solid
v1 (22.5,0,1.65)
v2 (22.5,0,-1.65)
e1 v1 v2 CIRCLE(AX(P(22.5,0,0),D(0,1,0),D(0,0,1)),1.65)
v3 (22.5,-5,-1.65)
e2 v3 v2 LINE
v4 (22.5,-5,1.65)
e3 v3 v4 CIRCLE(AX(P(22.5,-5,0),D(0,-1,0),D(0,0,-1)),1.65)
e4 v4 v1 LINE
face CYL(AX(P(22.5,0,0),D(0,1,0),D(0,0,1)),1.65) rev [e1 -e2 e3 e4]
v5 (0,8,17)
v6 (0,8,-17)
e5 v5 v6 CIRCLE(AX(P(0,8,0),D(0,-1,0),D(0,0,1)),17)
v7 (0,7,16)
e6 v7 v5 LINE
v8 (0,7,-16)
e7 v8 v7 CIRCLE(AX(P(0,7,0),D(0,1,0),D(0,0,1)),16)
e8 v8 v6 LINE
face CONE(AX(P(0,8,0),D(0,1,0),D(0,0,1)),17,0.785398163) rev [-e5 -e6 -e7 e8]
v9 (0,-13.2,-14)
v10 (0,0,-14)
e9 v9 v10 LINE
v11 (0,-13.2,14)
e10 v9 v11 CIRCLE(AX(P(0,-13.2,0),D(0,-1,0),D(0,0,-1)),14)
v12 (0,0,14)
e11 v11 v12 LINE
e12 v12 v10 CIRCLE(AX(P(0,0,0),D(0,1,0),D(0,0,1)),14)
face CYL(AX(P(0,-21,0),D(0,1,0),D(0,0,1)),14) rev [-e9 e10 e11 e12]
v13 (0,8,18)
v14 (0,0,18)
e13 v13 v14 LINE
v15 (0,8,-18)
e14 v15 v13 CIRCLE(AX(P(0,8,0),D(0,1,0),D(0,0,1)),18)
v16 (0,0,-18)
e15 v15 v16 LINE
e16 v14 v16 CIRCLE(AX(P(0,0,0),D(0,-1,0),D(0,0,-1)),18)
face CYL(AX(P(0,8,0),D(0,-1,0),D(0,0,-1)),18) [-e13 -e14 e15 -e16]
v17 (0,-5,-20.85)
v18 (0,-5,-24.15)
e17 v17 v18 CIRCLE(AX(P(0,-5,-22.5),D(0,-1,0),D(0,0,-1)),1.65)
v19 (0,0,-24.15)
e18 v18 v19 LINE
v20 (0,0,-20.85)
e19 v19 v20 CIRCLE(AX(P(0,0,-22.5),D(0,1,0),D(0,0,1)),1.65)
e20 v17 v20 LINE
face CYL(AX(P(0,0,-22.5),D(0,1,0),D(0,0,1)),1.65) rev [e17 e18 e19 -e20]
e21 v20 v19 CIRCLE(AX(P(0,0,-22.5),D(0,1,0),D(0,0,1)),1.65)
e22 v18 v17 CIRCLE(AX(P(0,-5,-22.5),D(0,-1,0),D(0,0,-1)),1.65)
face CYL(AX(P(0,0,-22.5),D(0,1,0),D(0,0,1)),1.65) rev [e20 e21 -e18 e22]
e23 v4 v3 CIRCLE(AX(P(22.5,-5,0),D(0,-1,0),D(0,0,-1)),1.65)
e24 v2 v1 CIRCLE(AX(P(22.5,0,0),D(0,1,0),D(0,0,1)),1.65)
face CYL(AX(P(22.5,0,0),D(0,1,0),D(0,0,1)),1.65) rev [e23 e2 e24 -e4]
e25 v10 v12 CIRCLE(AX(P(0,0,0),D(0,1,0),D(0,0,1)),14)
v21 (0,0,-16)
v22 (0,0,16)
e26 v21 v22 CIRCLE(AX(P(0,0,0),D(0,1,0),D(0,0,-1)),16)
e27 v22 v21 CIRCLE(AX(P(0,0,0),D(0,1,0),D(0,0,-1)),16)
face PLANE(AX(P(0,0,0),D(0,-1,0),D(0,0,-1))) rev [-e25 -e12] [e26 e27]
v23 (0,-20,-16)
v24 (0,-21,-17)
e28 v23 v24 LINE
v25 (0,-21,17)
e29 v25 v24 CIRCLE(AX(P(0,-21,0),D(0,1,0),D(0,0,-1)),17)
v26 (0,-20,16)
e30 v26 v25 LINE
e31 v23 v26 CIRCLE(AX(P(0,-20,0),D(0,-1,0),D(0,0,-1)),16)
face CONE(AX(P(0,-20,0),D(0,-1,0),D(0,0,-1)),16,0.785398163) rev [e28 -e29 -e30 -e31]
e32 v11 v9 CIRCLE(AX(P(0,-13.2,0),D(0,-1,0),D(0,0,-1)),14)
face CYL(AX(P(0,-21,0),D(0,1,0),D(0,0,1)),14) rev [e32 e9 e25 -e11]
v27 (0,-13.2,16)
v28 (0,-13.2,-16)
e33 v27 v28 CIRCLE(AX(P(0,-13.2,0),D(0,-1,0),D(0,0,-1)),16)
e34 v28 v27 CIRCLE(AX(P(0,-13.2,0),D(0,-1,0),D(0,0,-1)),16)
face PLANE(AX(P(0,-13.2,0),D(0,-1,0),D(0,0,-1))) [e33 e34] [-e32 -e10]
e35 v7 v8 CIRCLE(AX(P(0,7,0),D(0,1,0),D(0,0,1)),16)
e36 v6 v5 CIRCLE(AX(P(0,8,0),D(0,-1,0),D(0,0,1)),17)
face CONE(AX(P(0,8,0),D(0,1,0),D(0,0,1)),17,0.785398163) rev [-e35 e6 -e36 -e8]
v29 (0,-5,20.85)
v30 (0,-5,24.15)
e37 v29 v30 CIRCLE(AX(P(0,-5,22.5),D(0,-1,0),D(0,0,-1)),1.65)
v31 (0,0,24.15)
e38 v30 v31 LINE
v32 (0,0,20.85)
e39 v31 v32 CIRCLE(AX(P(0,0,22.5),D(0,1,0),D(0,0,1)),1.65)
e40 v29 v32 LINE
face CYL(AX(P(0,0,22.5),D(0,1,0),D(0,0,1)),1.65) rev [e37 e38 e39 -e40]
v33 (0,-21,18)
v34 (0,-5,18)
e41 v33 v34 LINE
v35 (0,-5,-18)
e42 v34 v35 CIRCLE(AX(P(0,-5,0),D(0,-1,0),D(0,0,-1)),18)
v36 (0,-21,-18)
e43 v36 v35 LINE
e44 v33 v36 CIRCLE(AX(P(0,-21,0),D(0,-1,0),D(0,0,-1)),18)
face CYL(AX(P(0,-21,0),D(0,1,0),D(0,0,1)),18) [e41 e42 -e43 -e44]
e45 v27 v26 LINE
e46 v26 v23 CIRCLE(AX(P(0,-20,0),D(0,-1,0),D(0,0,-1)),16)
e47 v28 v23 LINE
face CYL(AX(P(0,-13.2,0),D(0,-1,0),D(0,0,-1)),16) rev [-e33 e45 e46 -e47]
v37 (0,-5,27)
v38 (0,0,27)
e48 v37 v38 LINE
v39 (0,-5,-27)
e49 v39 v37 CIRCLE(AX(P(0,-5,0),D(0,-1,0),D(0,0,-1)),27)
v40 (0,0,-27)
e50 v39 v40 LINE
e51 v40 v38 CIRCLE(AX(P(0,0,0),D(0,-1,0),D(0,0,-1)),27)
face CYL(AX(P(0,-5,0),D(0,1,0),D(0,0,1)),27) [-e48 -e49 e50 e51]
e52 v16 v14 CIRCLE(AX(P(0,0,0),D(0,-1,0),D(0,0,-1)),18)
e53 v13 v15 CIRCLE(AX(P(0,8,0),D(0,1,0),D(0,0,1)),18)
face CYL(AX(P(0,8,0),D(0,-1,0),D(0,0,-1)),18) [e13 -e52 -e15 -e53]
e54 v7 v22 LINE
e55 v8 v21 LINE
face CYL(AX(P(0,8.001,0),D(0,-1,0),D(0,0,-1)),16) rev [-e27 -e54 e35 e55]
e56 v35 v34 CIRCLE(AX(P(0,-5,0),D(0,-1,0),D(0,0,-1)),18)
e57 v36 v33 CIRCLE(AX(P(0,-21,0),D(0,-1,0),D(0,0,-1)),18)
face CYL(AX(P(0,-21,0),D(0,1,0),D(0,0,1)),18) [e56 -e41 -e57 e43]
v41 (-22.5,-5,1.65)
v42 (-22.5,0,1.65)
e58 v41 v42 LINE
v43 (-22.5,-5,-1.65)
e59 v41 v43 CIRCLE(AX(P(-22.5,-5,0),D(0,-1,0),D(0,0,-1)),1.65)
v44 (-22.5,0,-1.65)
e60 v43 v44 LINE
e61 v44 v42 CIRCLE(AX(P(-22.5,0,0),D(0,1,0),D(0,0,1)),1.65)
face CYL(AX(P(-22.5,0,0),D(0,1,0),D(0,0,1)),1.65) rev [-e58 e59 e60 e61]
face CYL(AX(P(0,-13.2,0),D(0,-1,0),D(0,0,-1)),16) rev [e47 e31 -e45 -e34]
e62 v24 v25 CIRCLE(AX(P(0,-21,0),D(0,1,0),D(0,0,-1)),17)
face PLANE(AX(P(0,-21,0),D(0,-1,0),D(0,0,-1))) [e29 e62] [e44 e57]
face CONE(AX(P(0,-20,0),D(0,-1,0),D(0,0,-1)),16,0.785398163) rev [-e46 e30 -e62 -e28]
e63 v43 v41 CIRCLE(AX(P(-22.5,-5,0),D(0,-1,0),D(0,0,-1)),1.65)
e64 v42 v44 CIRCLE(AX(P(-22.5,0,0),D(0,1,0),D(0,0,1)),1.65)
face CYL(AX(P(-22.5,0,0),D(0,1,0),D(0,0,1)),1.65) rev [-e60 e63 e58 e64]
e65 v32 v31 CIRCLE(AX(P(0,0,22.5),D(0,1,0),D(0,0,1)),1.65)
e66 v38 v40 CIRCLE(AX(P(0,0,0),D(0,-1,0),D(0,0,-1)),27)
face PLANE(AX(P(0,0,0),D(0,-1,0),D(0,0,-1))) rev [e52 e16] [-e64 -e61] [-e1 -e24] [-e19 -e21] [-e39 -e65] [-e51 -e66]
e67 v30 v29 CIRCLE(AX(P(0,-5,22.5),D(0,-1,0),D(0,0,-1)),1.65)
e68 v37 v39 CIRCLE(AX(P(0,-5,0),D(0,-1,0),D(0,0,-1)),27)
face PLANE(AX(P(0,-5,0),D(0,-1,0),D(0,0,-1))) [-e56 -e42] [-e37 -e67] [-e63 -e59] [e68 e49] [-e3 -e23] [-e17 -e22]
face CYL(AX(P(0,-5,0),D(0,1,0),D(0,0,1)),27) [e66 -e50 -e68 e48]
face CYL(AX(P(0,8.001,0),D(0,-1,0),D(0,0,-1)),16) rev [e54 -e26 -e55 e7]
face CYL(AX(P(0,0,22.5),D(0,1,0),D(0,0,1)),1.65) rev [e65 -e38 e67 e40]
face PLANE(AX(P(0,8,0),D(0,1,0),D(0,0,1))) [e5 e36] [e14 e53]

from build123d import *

# Parameters (mm, degrees)
SKETCH1_R             = 18
BOSS_EXTRUDE1_DEPTH   = 8
CUT_EXTRUDE1_REACH    = 28.683
SKETCH2_R             = 16
SKETCH3_R             = 27
BOSS_EXTRUDE2_DEPTH   = 5
BOSS_EXTRUDE3_START   = 16
SKETCH4_R             = 18
BOSS_EXTRUDE3_DEPTH   = 16
SKETCH5_R             = 16
CUT_EXTRUDE2_DEPTH    = 7.8
SKETCH6_R             = 14
CUT_EXTRUDE3_DEPTH    = 44.577517139
M4_TAPPED_HOLE1_D     = 3.3
M4_TAPPED_HOLE1_DEPTH = 11.5
M4_TAPPED_HOLE1_TIP   = 0.991420021
CHAMFER1_SIZE         = 1


with BuildPart() as part:
    # Sketch1 → Boss-Extrude1 (new body)
    with BuildSketch(Plane(origin=(0, 0, 0), x_dir=(1, 0, 0), z_dir=(0, 1, 0))):
        with Locations(Location((0, 0, 0), (0, 0, 270))):
            Circle(SKETCH1_R)
    extrude(amount=BOSS_EXTRUDE1_DEPTH)

    # Sketch2 → Cut-Extrude1 (cut, up to next)
    with BuildSketch(Plane.XZ, mode=Mode.PRIVATE) as cut_extrude1_sk1:
        with Locations(Location((0, 0, 0), (0, 0, 270))):
            Circle(SKETCH2_R)
    cut_extrude1_tool1 = extrude(cut_extrude1_sk1.sketch, amount=-CUT_EXTRUDE1_REACH, mode=Mode.PRIVATE) & part.part
    add(cut_extrude1_tool1.solids().sort_by_distance((0, 0, 0))[0], mode=Mode.SUBTRACT)

    # Sketch3 → Boss-Extrude2 (add)
    with BuildSketch(Plane.XZ):
        with Locations(Location((0, 0, 0), (0, 0, 270))):
            Circle(SKETCH3_R)
    extrude(amount=BOSS_EXTRUDE2_DEPTH)

    # Sketch4 → Boss-Extrude3 (add)
    with BuildSketch(Plane.XZ.offset(5).offset(BOSS_EXTRUDE3_START)):
        with Locations(Location((0, 0, 0), (0, 0, 270))):
            Circle(SKETCH4_R)
    extrude(amount=-BOSS_EXTRUDE3_DEPTH)

    # Sketch5 → Cut-Extrude2 (cut)
    with BuildSketch(Plane.XZ.offset(21)):
        with Locations(Location((0, 0, 0), (0, 0, 270))):
            Circle(SKETCH5_R)
    extrude(amount=-CUT_EXTRUDE2_DEPTH, mode=Mode.SUBTRACT)

    # Sketch6 → Cut-Extrude3 (cut, through all)
    with BuildSketch(Plane(origin=(0, 0, 0), x_dir=(1, 0, 0), z_dir=(0, 1, 0))):
        with Locations(Location((0, 0, 0), (0, 0, 270))):
            Circle(SKETCH6_R)
    extrude(amount=-CUT_EXTRUDE3_DEPTH, mode=Mode.SUBTRACT)

    # M4 Tapped Hole1
    with Locations(Plane(origin=(0, 0, 0), x_dir=(1, 0, 0), z_dir=(0, 1, 0))):
        with Locations((-22.5, 0), (0, 0), (0, 22.5), (22.5, 0), (0, -22.5)):
            Hole(M4_TAPPED_HOLE1_D / 2, depth=M4_TAPPED_HOLE1_DEPTH)
            with Locations((0, 0, -(M4_TAPPED_HOLE1_DEPTH + M4_TAPPED_HOLE1_TIP / 2))):  # 118° drill point
                Cone(0, M4_TAPPED_HOLE1_D / 2, M4_TAPPED_HOLE1_TIP, mode=Mode.SUBTRACT)

    # Chamfer1
    chamfer1_edges = [part.edges().sort_by_distance(p)[0] for p in [
        (0, -21, 16),
        (0, 8, 16),
    ]]
    chamfer(chamfer1_edges, length=CHAMFER1_SIZE)


solid = part.part
